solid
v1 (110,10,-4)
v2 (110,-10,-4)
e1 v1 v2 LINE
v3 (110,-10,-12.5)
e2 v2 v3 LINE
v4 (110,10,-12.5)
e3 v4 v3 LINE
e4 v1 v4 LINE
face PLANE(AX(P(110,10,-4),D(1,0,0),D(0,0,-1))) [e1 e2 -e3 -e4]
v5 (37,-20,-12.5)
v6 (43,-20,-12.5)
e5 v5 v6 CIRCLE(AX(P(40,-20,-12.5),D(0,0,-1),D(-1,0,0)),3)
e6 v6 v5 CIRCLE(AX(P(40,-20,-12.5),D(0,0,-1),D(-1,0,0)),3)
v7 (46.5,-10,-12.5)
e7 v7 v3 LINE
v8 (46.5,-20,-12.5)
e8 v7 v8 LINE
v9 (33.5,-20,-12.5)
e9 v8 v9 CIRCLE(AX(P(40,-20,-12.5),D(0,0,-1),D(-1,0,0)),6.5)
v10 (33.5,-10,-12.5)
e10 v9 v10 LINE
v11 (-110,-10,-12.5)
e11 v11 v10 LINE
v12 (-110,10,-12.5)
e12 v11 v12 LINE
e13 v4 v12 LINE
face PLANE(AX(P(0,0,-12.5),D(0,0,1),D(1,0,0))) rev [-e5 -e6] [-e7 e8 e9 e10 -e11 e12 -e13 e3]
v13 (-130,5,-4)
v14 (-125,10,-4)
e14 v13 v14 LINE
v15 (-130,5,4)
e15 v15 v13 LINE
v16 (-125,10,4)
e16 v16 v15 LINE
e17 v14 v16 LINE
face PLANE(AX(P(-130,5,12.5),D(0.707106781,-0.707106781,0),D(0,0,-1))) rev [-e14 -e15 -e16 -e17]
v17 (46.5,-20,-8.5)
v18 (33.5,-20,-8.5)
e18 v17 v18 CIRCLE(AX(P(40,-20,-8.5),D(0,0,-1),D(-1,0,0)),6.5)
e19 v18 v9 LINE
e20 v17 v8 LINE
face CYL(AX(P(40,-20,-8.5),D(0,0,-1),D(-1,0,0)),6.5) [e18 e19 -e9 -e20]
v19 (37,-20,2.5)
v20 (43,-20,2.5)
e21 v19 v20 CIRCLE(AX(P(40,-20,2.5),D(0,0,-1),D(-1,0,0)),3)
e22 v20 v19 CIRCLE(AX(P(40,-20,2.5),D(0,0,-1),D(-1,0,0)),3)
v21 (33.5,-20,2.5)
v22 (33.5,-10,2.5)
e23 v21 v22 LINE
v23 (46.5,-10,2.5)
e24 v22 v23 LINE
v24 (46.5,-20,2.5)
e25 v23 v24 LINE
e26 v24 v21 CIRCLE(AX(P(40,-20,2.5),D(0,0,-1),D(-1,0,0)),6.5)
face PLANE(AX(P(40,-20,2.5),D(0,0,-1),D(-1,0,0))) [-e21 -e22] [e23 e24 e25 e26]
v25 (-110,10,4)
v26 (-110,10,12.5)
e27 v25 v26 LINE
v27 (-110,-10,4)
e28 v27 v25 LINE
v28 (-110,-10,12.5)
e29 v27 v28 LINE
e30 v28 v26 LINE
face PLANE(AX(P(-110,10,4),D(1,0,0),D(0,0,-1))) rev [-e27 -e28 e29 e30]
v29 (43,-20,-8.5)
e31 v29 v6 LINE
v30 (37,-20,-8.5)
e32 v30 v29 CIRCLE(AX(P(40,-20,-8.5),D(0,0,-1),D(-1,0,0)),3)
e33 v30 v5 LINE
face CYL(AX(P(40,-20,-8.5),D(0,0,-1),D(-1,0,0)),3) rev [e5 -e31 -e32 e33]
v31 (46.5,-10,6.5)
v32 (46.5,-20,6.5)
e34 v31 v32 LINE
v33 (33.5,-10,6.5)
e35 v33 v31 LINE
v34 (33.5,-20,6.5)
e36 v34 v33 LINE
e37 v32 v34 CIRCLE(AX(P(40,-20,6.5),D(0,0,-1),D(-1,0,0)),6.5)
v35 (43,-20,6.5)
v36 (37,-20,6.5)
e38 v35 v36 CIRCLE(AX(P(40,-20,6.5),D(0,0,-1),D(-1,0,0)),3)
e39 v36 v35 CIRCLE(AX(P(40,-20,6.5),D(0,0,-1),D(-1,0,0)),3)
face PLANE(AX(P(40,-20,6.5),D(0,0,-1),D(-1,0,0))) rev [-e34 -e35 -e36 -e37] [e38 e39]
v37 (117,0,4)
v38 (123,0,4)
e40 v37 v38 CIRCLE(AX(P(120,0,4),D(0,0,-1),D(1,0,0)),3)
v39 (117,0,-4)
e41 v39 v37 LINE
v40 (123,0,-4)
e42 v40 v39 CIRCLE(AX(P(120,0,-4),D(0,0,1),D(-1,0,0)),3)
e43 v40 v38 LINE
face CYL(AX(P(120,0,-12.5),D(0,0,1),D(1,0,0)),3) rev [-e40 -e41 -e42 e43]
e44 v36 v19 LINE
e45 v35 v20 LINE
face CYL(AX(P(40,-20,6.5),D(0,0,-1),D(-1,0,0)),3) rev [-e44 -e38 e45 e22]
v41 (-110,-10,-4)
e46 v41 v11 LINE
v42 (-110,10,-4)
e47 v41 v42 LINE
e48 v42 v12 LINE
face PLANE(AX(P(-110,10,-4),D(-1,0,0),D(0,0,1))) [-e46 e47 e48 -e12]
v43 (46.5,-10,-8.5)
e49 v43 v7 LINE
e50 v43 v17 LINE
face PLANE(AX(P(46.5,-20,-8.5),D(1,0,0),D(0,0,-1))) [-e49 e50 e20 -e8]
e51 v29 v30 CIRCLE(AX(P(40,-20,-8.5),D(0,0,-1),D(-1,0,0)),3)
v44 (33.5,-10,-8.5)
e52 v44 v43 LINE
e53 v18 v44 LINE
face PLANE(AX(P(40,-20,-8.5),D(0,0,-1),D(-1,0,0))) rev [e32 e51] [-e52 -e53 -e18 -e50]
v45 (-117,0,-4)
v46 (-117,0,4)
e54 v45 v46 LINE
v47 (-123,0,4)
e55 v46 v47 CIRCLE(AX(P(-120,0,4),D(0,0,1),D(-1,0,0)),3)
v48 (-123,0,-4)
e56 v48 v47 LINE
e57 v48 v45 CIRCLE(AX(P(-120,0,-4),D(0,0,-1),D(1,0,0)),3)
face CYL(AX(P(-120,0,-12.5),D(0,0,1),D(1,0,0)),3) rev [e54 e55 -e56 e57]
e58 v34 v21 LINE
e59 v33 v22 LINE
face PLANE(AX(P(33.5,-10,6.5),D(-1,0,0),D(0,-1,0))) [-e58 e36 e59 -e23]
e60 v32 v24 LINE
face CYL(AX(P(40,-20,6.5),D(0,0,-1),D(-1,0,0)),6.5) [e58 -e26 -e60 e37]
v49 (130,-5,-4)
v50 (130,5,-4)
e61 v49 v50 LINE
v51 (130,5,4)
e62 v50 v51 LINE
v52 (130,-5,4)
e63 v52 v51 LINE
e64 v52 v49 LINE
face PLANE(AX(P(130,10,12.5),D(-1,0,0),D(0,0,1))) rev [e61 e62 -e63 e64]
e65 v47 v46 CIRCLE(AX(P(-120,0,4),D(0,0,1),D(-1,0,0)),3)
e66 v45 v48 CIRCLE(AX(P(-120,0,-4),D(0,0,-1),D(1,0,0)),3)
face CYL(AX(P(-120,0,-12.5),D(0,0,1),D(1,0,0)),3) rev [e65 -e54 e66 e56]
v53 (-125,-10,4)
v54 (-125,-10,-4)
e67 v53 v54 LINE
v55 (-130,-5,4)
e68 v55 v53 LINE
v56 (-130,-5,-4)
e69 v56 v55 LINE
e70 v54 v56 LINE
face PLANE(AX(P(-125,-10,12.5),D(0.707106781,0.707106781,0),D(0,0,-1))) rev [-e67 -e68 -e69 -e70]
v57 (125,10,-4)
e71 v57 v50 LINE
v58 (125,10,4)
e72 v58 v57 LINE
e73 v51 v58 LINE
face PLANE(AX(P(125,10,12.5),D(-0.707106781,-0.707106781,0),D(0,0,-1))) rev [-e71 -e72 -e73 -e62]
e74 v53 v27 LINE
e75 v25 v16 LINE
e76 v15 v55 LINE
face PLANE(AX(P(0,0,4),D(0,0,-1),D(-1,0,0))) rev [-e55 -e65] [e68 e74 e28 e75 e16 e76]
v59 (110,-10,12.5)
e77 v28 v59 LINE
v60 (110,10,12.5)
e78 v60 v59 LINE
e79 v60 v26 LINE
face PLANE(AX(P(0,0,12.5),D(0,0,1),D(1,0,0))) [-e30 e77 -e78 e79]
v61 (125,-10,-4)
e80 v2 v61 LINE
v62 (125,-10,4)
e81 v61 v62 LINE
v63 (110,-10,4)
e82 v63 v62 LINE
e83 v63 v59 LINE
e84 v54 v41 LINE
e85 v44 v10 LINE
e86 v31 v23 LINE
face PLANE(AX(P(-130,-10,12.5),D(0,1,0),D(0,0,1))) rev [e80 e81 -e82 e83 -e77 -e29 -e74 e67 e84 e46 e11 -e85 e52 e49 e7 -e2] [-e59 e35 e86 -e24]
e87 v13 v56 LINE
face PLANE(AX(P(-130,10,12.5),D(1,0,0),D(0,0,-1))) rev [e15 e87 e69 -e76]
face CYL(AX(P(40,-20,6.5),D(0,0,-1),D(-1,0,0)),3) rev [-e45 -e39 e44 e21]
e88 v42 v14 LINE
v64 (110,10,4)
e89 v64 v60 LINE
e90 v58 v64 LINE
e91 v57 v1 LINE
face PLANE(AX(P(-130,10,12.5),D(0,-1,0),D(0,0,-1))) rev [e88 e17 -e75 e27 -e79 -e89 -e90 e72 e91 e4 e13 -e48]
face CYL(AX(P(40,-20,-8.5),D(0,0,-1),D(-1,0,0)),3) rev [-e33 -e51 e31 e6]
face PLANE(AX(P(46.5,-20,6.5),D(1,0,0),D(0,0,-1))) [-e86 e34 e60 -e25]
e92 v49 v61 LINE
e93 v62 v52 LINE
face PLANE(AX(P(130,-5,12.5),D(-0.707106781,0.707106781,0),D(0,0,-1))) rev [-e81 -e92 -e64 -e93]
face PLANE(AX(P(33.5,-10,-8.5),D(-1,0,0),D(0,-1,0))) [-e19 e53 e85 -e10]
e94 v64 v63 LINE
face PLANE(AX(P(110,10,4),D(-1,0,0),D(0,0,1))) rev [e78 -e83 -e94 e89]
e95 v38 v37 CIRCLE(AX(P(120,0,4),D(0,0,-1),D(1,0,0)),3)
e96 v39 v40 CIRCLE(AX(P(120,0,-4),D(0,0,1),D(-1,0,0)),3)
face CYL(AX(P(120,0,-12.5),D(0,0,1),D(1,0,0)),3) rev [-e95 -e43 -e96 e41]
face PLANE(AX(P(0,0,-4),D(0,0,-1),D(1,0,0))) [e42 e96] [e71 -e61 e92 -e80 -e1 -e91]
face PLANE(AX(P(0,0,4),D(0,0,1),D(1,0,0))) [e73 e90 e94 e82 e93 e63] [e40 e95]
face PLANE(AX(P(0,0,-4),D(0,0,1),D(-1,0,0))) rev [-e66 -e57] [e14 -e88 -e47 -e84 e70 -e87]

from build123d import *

# Parameters (mm, degrees)
SKETCH1_W           = 260
SKETCH1_H           = 20
BOSS_EXTRUDE1_DEPTH = 12.5
SKETCH2_R           = 3
CUT_EXTRUDE1_DEPTH  = 133.759180474
SKETCH3_W           = 20
SKETCH3_H           = 20
CUT_EXTRUDE2_DEPTH  = 8.5
CHAMFER1_SIZE       = 5
SKETCH4_R           = 3
BOSS_EXTRUDE2_DEPTH = 4
LPATTERN1_COUNT     = 2
LPATTERN1_PITCH     = 15


with BuildPart() as part:
    # Sketch1 → Boss-Extrude1 (new, symmetric)
    with BuildSketch(Plane.XY):
        Rectangle(SKETCH1_W, SKETCH1_H)
    extrude(amount=BOSS_EXTRUDE1_DEPTH, both=True)

    # Sketch2 → Cut-Extrude1 (cut, through all)
    with BuildSketch(Plane.XY.offset(12.5)):
        with Locations((-120, 0)):
            Circle(SKETCH2_R)
        with Locations((120, 0)):
            Circle(SKETCH2_R)
    extrude(amount=-CUT_EXTRUDE1_DEPTH, mode=Mode.SUBTRACT)

    # Sketch3 → Cut-Extrude2 (cut)
    with BuildSketch(Plane.XY.offset(12.5)):
        with Locations((-120, 0)):
            Rectangle(SKETCH3_W, SKETCH3_H)
        with Locations((120, 0)):
            Rectangle(SKETCH3_W, SKETCH3_H)
    cut_extrude2 = extrude(amount=-CUT_EXTRUDE2_DEPTH, mode=Mode.SUBTRACT)

    # Mirror2: Cut-Extrude2 across plane
    add(cut_extrude2.mirror(Plane.XY), mode=Mode.SUBTRACT)

    # Chamfer1
    chamfer1_edges = [part.edges().sort_by_distance(p)[0] for p in [
        (130, -10, 0),
        (-130, -10, 0),
        (-130, 10, 0),
        (130, 10, 0),
    ]]
    chamfer(chamfer1_edges, length=CHAMFER1_SIZE)

    # Sketch4 → Boss-Extrude2 (add)
    with BuildSketch(Plane(origin=(0, 0, -12.5), x_dir=(-1, 0, 0), z_dir=(0, 0, -1))):
        with BuildLine():
            Line((-46.5, -20), (-46.5, -10))
            Line((-46.5, -10), (-33.5, -10))
            Line((-33.5, -10), (-33.5, -20))
            ThreePointArc((-33.5, -20), (-40, -26.5), (-46.5, -20))
        make_face()
        with Locations((-40, -20)):
            Circle(SKETCH4_R, mode=Mode.SUBTRACT)
    boss_extrude2 = extrude(amount=-BOSS_EXTRUDE2_DEPTH)

    # LPattern1: Boss-Extrude2 ×2
    with Locations(*[(0, 0, i * LPATTERN1_PITCH) for i in range(1, LPATTERN1_COUNT)]):
        add(boss_extrude2)


solid = part.part
